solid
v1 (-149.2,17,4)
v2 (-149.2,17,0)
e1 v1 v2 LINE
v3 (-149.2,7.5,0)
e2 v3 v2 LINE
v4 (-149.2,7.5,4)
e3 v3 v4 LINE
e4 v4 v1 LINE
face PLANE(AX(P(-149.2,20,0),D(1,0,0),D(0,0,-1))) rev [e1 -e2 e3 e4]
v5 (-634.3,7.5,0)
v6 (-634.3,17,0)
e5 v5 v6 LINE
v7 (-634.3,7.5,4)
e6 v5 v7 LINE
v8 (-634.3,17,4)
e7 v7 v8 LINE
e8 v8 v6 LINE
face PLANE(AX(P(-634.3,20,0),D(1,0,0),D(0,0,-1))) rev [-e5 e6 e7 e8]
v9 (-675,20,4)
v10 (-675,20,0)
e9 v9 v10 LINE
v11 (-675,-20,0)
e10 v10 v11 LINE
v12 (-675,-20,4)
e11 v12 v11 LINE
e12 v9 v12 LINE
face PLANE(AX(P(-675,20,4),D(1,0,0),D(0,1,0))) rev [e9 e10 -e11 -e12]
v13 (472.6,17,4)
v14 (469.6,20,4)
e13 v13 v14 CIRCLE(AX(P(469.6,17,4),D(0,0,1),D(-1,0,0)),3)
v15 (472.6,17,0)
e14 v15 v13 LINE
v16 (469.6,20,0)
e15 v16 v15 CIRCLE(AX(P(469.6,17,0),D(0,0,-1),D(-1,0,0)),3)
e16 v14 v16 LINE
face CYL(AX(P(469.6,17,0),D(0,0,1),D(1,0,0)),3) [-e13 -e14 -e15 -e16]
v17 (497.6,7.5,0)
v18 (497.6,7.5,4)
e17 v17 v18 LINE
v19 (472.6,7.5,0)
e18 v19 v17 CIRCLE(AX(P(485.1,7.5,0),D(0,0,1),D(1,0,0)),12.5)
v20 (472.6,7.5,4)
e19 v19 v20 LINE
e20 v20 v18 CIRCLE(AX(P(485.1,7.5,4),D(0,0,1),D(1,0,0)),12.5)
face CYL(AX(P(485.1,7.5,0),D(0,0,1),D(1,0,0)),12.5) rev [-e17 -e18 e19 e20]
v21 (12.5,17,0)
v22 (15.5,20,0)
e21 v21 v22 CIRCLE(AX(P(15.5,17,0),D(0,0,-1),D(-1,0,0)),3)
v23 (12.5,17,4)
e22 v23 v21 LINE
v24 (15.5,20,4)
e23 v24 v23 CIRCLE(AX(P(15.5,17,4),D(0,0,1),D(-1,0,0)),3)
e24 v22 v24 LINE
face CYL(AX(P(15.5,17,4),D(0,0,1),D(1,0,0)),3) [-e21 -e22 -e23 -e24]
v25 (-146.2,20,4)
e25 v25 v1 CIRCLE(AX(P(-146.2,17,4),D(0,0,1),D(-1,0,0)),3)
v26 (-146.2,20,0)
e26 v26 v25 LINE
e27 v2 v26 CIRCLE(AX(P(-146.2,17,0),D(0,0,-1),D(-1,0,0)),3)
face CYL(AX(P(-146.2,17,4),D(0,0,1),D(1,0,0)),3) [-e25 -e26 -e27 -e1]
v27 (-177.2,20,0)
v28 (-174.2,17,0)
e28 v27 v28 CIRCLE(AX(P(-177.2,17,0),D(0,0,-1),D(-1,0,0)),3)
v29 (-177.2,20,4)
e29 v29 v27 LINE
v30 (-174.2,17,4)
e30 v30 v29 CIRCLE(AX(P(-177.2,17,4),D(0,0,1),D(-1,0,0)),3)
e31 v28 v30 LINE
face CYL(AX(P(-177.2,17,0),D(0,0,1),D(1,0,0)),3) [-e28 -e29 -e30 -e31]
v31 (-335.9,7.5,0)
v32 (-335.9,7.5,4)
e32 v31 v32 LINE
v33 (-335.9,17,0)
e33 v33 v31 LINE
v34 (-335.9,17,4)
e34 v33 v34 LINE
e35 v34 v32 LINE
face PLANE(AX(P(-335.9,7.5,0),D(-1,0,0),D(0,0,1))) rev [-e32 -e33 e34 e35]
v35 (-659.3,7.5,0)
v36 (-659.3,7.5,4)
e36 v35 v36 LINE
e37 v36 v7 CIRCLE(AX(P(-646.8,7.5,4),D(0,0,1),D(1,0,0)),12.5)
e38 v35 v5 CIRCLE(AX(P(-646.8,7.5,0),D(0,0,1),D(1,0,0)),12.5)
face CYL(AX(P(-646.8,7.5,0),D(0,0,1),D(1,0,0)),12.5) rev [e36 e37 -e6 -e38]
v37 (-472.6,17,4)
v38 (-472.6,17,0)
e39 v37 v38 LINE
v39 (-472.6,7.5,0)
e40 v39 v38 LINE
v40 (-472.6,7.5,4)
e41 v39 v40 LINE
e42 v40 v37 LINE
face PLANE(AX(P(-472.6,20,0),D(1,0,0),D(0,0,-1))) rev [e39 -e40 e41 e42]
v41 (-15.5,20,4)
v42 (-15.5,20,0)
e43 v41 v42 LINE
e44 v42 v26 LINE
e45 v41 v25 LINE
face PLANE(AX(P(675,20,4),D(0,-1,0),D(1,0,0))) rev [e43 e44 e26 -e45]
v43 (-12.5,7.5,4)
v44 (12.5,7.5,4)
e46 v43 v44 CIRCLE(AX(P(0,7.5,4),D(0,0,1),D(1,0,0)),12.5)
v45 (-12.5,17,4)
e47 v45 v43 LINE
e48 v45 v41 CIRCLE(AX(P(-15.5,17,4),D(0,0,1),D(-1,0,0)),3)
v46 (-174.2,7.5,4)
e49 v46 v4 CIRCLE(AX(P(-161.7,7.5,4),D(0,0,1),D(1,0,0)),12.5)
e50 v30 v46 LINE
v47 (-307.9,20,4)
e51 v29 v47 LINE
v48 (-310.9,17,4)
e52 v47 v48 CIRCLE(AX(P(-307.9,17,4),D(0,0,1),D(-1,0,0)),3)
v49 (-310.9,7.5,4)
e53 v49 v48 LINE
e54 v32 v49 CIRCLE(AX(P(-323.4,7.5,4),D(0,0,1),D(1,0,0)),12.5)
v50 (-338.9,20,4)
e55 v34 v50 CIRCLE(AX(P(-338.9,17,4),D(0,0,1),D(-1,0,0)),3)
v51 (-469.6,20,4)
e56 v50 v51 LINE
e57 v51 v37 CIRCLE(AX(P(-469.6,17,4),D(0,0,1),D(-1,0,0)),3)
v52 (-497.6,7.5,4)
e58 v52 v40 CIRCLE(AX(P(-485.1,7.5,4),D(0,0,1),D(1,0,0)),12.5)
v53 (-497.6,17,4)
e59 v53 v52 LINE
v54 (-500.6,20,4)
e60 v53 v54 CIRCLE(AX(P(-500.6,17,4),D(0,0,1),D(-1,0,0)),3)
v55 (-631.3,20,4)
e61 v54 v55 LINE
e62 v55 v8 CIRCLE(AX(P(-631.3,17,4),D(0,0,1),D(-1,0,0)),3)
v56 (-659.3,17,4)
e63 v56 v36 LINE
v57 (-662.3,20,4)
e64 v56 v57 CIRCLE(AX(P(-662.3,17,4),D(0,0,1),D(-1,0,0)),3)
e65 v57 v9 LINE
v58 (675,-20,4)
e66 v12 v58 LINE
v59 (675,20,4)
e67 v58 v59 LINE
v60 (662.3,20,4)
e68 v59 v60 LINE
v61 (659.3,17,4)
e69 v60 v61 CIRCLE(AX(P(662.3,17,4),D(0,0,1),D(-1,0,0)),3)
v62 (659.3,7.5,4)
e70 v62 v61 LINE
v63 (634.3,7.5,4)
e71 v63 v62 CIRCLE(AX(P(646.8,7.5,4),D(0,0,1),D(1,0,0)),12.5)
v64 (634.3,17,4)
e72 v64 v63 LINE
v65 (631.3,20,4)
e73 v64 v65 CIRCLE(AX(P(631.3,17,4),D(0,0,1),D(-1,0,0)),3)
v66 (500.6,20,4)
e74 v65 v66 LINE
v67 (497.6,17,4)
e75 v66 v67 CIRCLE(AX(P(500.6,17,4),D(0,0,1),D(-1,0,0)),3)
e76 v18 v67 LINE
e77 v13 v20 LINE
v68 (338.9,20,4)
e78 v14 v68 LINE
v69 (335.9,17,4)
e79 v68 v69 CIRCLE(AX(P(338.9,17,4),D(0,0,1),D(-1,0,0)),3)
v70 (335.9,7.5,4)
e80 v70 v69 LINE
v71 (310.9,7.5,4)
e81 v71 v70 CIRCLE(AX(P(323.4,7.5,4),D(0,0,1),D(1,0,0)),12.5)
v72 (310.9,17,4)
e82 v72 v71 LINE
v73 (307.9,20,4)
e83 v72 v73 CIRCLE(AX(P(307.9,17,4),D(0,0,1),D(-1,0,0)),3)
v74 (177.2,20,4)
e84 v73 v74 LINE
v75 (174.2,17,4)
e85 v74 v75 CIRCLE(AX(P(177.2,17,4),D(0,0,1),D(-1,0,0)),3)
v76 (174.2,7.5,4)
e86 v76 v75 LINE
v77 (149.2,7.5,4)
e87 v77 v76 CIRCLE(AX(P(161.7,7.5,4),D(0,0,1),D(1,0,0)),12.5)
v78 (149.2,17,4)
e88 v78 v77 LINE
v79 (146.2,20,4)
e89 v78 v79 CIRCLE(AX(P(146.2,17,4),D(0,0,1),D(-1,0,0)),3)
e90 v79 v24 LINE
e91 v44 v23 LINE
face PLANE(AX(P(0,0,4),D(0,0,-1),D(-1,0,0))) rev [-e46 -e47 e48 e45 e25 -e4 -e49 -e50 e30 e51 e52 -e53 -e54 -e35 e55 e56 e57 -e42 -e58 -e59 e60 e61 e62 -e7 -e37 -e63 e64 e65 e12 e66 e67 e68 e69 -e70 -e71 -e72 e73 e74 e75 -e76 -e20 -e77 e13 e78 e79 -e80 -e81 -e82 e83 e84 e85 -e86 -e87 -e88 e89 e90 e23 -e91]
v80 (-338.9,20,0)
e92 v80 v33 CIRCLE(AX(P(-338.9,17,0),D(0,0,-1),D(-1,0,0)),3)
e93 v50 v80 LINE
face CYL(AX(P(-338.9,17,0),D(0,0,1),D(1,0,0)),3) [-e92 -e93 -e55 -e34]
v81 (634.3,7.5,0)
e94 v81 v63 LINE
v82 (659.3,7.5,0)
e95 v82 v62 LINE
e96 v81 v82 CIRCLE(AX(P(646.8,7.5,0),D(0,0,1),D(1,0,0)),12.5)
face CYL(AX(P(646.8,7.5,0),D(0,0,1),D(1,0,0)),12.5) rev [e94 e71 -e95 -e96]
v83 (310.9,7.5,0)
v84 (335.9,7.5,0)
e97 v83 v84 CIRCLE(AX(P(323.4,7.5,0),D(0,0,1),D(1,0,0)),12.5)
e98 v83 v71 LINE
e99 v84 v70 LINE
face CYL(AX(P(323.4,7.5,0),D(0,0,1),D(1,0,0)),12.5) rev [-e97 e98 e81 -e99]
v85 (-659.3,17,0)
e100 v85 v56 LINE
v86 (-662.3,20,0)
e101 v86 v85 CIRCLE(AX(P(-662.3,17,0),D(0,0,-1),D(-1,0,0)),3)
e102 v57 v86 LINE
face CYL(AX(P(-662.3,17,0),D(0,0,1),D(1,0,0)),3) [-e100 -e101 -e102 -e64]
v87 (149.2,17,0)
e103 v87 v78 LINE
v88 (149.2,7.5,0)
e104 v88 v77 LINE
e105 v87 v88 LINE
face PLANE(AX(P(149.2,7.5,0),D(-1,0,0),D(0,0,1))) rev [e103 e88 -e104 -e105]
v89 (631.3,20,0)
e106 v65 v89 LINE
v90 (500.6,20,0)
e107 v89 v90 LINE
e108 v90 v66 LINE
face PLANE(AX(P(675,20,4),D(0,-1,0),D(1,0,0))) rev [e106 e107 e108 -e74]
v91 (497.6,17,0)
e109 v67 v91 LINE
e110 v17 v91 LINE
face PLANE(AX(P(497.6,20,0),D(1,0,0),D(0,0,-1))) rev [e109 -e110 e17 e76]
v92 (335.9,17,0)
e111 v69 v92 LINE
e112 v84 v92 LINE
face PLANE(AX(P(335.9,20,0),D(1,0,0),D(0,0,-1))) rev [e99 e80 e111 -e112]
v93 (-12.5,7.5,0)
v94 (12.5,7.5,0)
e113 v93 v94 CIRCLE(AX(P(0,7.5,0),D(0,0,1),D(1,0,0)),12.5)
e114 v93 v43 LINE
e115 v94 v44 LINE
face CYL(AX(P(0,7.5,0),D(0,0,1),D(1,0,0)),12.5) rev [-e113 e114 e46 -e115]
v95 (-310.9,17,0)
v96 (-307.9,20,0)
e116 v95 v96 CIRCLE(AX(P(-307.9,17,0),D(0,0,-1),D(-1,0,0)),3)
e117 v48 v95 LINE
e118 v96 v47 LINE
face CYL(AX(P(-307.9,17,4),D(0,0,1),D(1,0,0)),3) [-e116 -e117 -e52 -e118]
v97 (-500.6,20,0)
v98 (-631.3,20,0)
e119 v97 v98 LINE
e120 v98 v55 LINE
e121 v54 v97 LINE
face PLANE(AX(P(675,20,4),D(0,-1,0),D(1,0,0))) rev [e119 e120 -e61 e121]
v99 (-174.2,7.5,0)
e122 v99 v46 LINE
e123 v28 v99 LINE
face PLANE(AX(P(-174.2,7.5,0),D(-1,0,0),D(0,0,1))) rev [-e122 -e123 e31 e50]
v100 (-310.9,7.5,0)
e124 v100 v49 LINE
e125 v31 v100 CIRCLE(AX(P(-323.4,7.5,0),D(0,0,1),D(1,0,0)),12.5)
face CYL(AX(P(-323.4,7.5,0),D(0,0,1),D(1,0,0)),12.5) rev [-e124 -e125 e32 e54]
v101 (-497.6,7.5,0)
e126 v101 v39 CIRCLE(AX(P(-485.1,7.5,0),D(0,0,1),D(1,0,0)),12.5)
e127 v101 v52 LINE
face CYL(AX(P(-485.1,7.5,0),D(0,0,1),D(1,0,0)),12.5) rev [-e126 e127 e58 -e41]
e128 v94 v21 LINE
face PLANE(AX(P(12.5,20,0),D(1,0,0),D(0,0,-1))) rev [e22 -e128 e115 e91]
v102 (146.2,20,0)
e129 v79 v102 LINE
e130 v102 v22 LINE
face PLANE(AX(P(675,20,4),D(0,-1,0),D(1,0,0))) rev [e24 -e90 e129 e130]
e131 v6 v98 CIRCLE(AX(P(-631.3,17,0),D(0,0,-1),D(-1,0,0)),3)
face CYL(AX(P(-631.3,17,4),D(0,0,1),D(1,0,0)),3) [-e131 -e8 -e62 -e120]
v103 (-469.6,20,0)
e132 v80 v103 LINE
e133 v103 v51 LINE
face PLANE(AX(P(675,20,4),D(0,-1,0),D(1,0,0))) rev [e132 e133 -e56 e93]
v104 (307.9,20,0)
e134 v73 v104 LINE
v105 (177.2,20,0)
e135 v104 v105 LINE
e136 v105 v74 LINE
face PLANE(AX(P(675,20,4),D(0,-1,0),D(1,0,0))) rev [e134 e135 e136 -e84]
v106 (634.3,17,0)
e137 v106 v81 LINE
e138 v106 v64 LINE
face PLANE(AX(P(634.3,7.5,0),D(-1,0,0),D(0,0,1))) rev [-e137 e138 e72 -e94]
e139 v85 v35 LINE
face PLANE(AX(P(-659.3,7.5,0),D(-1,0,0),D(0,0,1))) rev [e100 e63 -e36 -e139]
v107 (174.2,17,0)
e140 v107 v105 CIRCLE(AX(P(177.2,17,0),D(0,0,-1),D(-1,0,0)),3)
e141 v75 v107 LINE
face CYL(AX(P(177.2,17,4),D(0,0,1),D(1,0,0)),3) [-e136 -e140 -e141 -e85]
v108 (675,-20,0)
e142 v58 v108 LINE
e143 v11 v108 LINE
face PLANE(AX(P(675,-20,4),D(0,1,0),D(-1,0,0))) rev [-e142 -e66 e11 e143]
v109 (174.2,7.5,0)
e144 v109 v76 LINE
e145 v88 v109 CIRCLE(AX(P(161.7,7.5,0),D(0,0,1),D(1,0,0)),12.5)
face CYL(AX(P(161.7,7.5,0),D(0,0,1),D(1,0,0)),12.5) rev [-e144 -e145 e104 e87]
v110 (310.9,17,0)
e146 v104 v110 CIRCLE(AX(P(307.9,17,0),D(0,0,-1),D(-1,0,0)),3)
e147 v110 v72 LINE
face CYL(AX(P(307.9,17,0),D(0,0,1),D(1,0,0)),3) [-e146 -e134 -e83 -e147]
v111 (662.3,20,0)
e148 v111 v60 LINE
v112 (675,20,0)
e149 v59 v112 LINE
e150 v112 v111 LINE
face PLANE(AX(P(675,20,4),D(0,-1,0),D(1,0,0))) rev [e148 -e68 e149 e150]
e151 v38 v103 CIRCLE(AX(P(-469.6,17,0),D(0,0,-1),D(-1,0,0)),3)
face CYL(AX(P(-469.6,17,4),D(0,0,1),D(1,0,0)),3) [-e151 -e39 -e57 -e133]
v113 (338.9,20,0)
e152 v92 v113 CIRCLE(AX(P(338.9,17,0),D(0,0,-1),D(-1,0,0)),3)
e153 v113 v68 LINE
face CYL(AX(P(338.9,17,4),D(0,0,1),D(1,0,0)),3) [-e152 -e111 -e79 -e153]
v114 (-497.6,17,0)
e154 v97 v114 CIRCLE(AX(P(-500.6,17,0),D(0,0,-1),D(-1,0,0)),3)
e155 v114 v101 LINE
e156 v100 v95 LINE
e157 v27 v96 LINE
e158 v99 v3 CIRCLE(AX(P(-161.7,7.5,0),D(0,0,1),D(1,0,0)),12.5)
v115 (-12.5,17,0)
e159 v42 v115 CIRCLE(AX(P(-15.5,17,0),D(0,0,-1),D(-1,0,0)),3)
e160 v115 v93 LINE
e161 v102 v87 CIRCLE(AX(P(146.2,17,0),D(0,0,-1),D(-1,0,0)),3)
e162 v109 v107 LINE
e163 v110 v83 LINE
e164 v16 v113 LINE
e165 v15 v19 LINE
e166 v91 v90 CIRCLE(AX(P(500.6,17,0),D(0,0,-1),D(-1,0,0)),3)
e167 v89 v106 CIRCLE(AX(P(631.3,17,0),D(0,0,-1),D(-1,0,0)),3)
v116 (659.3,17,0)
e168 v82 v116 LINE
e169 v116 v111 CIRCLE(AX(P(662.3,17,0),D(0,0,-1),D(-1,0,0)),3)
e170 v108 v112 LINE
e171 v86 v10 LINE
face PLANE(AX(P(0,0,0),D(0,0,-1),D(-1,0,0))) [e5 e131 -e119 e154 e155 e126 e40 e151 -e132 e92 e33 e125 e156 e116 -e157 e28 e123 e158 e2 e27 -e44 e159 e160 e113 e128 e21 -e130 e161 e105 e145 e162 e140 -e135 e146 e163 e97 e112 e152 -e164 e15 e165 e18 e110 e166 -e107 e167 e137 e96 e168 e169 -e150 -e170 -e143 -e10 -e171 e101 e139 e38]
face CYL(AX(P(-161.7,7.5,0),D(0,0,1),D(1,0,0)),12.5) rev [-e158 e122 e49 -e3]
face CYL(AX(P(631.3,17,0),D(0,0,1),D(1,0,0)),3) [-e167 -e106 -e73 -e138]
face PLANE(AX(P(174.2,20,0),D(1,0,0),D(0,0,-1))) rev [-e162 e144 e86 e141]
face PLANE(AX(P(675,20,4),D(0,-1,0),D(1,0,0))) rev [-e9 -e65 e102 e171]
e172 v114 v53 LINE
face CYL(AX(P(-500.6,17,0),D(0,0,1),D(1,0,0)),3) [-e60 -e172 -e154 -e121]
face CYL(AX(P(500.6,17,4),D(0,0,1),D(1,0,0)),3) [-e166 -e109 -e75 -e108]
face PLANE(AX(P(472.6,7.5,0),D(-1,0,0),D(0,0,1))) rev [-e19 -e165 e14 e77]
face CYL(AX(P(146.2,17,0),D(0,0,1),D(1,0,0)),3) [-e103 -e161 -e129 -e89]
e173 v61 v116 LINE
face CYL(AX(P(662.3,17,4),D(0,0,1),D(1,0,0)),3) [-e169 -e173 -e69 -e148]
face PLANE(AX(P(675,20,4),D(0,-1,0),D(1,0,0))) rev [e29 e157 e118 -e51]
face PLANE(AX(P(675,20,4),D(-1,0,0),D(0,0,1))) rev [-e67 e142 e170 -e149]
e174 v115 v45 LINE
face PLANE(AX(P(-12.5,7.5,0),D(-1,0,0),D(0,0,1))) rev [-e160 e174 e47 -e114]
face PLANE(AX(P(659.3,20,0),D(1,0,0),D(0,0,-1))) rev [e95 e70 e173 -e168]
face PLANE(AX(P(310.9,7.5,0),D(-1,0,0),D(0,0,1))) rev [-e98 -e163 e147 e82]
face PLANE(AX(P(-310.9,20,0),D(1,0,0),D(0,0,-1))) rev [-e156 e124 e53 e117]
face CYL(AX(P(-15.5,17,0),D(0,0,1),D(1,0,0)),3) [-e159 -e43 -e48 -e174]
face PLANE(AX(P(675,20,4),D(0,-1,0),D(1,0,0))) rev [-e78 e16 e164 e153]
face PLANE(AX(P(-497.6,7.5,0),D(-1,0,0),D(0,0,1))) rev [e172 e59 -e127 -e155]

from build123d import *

# Parameters (mm, degrees)
SKETCH1_W           = 1350
SKETCH1_H           = 40
BOSS_EXTRUDE1_DEPTH = 4
CUT_EXTRUDE1_DEPTH  = 4
FILLET1_R           = 3


with BuildPart() as part:
    # Sketch1 → Boss-Extrude1 (new body)
    with BuildSketch(Plane.XY):
        Rectangle(SKETCH1_W, SKETCH1_H)
    extrude(amount=BOSS_EXTRUDE1_DEPTH)

    # Sketch2 → Cut-Extrude1 (cut)
    with BuildSketch(Plane.XY.offset(4)):
        with BuildLine():
            Line((-659.3, 7.5), (-659.3, 20))
            Line((-659.3, 20), (-634.3, 20))
            Line((-634.3, 20), (-634.3, 7.5))
            ThreePointArc((-634.3, 7.5), (-646.8, -5), (-659.3, 7.5))
        make_face()
        with BuildLine():
            Line((-497.6, 7.5), (-497.6, 20))
            Line((-497.6, 20), (-472.6, 20))
            Line((-472.6, 20), (-472.6, 7.5))
            ThreePointArc((-472.6, 7.5), (-485.1, -5), (-497.6, 7.5))
        make_face()
        with BuildLine():
            Line((-335.9, 7.5), (-335.9, 20))
            Line((-335.9, 20), (-310.9, 20))
            Line((-310.9, 20), (-310.9, 7.5))
            ThreePointArc((-310.9, 7.5), (-323.4, -5), (-335.9, 7.5))
        make_face()
        with BuildLine():
            Line((-174.2, 7.5), (-174.2, 20))
            Line((-174.2, 20), (-149.2, 20))
            Line((-149.2, 20), (-149.2, 7.5))
            ThreePointArc((-149.2, 7.5), (-161.7, -5), (-174.2, 7.5))
        make_face()
        with BuildLine():
            Line((-12.5, 7.5), (-12.5, 20))
            Line((-12.5, 20), (12.5, 20))
            Line((12.5, 20), (12.5, 7.5))
            ThreePointArc((12.5, 7.5), (0, -5), (-12.5, 7.5))
        make_face()
        with BuildLine():
            Line((149.2, 7.5), (149.2, 20))
            Line((149.2, 20), (174.2, 20))
            Line((174.2, 20), (174.2, 7.5))
            ThreePointArc((174.2, 7.5), (161.7, -5), (149.2, 7.5))
        make_face()
        with BuildLine():
            Line((310.9, 7.5), (310.9, 20))
            Line((310.9, 20), (335.9, 20))
            Line((335.9, 20), (335.9, 7.5))
            ThreePointArc((335.9, 7.5), (323.4, -5), (310.9, 7.5))
        make_face()
        with BuildLine():
            Line((472.6, 7.5), (472.6, 20))
            Line((472.6, 20), (497.6, 20))
            Line((497.6, 20), (497.6, 7.5))
            ThreePointArc((497.6, 7.5), (485.1, -5), (472.6, 7.5))
        make_face()
        with BuildLine():
            Line((634.3, 7.5), (634.3, 20))
            Line((634.3, 20), (659.3, 20))
            Line((659.3, 20), (659.3, 7.5))
            ThreePointArc((659.3, 7.5), (646.8, -5), (634.3, 7.5))
        make_face()
    extrude(amount=-CUT_EXTRUDE1_DEPTH, mode=Mode.SUBTRACT)

    # Fillet1
    fillet1_edges = [part.edges().sort_by_distance(p)[0] for p in [
        (497.6, 20, 2),
        (634.3, 20, 2),
        (659.3, 20, 2),
        (-659.3, 20, 2),
        (-634.3, 20, 2),
        (-497.6, 20, 2),
        (-472.6, 20, 2),
        (-335.9, 20, 2),
        (-310.9, 20, 2),
        (-174.2, 20, 2),
        (-149.2, 20, 2),
        (-12.5, 20, 2),
        (12.5, 20, 2),
        (149.2, 20, 2),
        (174.2, 20, 2),
        (310.9, 20, 2),
        (335.9, 20, 2),
        (472.6, 20, 2),
    ]]
    fillet(fillet1_edges, radius=FILLET1_R)


solid = part.part
